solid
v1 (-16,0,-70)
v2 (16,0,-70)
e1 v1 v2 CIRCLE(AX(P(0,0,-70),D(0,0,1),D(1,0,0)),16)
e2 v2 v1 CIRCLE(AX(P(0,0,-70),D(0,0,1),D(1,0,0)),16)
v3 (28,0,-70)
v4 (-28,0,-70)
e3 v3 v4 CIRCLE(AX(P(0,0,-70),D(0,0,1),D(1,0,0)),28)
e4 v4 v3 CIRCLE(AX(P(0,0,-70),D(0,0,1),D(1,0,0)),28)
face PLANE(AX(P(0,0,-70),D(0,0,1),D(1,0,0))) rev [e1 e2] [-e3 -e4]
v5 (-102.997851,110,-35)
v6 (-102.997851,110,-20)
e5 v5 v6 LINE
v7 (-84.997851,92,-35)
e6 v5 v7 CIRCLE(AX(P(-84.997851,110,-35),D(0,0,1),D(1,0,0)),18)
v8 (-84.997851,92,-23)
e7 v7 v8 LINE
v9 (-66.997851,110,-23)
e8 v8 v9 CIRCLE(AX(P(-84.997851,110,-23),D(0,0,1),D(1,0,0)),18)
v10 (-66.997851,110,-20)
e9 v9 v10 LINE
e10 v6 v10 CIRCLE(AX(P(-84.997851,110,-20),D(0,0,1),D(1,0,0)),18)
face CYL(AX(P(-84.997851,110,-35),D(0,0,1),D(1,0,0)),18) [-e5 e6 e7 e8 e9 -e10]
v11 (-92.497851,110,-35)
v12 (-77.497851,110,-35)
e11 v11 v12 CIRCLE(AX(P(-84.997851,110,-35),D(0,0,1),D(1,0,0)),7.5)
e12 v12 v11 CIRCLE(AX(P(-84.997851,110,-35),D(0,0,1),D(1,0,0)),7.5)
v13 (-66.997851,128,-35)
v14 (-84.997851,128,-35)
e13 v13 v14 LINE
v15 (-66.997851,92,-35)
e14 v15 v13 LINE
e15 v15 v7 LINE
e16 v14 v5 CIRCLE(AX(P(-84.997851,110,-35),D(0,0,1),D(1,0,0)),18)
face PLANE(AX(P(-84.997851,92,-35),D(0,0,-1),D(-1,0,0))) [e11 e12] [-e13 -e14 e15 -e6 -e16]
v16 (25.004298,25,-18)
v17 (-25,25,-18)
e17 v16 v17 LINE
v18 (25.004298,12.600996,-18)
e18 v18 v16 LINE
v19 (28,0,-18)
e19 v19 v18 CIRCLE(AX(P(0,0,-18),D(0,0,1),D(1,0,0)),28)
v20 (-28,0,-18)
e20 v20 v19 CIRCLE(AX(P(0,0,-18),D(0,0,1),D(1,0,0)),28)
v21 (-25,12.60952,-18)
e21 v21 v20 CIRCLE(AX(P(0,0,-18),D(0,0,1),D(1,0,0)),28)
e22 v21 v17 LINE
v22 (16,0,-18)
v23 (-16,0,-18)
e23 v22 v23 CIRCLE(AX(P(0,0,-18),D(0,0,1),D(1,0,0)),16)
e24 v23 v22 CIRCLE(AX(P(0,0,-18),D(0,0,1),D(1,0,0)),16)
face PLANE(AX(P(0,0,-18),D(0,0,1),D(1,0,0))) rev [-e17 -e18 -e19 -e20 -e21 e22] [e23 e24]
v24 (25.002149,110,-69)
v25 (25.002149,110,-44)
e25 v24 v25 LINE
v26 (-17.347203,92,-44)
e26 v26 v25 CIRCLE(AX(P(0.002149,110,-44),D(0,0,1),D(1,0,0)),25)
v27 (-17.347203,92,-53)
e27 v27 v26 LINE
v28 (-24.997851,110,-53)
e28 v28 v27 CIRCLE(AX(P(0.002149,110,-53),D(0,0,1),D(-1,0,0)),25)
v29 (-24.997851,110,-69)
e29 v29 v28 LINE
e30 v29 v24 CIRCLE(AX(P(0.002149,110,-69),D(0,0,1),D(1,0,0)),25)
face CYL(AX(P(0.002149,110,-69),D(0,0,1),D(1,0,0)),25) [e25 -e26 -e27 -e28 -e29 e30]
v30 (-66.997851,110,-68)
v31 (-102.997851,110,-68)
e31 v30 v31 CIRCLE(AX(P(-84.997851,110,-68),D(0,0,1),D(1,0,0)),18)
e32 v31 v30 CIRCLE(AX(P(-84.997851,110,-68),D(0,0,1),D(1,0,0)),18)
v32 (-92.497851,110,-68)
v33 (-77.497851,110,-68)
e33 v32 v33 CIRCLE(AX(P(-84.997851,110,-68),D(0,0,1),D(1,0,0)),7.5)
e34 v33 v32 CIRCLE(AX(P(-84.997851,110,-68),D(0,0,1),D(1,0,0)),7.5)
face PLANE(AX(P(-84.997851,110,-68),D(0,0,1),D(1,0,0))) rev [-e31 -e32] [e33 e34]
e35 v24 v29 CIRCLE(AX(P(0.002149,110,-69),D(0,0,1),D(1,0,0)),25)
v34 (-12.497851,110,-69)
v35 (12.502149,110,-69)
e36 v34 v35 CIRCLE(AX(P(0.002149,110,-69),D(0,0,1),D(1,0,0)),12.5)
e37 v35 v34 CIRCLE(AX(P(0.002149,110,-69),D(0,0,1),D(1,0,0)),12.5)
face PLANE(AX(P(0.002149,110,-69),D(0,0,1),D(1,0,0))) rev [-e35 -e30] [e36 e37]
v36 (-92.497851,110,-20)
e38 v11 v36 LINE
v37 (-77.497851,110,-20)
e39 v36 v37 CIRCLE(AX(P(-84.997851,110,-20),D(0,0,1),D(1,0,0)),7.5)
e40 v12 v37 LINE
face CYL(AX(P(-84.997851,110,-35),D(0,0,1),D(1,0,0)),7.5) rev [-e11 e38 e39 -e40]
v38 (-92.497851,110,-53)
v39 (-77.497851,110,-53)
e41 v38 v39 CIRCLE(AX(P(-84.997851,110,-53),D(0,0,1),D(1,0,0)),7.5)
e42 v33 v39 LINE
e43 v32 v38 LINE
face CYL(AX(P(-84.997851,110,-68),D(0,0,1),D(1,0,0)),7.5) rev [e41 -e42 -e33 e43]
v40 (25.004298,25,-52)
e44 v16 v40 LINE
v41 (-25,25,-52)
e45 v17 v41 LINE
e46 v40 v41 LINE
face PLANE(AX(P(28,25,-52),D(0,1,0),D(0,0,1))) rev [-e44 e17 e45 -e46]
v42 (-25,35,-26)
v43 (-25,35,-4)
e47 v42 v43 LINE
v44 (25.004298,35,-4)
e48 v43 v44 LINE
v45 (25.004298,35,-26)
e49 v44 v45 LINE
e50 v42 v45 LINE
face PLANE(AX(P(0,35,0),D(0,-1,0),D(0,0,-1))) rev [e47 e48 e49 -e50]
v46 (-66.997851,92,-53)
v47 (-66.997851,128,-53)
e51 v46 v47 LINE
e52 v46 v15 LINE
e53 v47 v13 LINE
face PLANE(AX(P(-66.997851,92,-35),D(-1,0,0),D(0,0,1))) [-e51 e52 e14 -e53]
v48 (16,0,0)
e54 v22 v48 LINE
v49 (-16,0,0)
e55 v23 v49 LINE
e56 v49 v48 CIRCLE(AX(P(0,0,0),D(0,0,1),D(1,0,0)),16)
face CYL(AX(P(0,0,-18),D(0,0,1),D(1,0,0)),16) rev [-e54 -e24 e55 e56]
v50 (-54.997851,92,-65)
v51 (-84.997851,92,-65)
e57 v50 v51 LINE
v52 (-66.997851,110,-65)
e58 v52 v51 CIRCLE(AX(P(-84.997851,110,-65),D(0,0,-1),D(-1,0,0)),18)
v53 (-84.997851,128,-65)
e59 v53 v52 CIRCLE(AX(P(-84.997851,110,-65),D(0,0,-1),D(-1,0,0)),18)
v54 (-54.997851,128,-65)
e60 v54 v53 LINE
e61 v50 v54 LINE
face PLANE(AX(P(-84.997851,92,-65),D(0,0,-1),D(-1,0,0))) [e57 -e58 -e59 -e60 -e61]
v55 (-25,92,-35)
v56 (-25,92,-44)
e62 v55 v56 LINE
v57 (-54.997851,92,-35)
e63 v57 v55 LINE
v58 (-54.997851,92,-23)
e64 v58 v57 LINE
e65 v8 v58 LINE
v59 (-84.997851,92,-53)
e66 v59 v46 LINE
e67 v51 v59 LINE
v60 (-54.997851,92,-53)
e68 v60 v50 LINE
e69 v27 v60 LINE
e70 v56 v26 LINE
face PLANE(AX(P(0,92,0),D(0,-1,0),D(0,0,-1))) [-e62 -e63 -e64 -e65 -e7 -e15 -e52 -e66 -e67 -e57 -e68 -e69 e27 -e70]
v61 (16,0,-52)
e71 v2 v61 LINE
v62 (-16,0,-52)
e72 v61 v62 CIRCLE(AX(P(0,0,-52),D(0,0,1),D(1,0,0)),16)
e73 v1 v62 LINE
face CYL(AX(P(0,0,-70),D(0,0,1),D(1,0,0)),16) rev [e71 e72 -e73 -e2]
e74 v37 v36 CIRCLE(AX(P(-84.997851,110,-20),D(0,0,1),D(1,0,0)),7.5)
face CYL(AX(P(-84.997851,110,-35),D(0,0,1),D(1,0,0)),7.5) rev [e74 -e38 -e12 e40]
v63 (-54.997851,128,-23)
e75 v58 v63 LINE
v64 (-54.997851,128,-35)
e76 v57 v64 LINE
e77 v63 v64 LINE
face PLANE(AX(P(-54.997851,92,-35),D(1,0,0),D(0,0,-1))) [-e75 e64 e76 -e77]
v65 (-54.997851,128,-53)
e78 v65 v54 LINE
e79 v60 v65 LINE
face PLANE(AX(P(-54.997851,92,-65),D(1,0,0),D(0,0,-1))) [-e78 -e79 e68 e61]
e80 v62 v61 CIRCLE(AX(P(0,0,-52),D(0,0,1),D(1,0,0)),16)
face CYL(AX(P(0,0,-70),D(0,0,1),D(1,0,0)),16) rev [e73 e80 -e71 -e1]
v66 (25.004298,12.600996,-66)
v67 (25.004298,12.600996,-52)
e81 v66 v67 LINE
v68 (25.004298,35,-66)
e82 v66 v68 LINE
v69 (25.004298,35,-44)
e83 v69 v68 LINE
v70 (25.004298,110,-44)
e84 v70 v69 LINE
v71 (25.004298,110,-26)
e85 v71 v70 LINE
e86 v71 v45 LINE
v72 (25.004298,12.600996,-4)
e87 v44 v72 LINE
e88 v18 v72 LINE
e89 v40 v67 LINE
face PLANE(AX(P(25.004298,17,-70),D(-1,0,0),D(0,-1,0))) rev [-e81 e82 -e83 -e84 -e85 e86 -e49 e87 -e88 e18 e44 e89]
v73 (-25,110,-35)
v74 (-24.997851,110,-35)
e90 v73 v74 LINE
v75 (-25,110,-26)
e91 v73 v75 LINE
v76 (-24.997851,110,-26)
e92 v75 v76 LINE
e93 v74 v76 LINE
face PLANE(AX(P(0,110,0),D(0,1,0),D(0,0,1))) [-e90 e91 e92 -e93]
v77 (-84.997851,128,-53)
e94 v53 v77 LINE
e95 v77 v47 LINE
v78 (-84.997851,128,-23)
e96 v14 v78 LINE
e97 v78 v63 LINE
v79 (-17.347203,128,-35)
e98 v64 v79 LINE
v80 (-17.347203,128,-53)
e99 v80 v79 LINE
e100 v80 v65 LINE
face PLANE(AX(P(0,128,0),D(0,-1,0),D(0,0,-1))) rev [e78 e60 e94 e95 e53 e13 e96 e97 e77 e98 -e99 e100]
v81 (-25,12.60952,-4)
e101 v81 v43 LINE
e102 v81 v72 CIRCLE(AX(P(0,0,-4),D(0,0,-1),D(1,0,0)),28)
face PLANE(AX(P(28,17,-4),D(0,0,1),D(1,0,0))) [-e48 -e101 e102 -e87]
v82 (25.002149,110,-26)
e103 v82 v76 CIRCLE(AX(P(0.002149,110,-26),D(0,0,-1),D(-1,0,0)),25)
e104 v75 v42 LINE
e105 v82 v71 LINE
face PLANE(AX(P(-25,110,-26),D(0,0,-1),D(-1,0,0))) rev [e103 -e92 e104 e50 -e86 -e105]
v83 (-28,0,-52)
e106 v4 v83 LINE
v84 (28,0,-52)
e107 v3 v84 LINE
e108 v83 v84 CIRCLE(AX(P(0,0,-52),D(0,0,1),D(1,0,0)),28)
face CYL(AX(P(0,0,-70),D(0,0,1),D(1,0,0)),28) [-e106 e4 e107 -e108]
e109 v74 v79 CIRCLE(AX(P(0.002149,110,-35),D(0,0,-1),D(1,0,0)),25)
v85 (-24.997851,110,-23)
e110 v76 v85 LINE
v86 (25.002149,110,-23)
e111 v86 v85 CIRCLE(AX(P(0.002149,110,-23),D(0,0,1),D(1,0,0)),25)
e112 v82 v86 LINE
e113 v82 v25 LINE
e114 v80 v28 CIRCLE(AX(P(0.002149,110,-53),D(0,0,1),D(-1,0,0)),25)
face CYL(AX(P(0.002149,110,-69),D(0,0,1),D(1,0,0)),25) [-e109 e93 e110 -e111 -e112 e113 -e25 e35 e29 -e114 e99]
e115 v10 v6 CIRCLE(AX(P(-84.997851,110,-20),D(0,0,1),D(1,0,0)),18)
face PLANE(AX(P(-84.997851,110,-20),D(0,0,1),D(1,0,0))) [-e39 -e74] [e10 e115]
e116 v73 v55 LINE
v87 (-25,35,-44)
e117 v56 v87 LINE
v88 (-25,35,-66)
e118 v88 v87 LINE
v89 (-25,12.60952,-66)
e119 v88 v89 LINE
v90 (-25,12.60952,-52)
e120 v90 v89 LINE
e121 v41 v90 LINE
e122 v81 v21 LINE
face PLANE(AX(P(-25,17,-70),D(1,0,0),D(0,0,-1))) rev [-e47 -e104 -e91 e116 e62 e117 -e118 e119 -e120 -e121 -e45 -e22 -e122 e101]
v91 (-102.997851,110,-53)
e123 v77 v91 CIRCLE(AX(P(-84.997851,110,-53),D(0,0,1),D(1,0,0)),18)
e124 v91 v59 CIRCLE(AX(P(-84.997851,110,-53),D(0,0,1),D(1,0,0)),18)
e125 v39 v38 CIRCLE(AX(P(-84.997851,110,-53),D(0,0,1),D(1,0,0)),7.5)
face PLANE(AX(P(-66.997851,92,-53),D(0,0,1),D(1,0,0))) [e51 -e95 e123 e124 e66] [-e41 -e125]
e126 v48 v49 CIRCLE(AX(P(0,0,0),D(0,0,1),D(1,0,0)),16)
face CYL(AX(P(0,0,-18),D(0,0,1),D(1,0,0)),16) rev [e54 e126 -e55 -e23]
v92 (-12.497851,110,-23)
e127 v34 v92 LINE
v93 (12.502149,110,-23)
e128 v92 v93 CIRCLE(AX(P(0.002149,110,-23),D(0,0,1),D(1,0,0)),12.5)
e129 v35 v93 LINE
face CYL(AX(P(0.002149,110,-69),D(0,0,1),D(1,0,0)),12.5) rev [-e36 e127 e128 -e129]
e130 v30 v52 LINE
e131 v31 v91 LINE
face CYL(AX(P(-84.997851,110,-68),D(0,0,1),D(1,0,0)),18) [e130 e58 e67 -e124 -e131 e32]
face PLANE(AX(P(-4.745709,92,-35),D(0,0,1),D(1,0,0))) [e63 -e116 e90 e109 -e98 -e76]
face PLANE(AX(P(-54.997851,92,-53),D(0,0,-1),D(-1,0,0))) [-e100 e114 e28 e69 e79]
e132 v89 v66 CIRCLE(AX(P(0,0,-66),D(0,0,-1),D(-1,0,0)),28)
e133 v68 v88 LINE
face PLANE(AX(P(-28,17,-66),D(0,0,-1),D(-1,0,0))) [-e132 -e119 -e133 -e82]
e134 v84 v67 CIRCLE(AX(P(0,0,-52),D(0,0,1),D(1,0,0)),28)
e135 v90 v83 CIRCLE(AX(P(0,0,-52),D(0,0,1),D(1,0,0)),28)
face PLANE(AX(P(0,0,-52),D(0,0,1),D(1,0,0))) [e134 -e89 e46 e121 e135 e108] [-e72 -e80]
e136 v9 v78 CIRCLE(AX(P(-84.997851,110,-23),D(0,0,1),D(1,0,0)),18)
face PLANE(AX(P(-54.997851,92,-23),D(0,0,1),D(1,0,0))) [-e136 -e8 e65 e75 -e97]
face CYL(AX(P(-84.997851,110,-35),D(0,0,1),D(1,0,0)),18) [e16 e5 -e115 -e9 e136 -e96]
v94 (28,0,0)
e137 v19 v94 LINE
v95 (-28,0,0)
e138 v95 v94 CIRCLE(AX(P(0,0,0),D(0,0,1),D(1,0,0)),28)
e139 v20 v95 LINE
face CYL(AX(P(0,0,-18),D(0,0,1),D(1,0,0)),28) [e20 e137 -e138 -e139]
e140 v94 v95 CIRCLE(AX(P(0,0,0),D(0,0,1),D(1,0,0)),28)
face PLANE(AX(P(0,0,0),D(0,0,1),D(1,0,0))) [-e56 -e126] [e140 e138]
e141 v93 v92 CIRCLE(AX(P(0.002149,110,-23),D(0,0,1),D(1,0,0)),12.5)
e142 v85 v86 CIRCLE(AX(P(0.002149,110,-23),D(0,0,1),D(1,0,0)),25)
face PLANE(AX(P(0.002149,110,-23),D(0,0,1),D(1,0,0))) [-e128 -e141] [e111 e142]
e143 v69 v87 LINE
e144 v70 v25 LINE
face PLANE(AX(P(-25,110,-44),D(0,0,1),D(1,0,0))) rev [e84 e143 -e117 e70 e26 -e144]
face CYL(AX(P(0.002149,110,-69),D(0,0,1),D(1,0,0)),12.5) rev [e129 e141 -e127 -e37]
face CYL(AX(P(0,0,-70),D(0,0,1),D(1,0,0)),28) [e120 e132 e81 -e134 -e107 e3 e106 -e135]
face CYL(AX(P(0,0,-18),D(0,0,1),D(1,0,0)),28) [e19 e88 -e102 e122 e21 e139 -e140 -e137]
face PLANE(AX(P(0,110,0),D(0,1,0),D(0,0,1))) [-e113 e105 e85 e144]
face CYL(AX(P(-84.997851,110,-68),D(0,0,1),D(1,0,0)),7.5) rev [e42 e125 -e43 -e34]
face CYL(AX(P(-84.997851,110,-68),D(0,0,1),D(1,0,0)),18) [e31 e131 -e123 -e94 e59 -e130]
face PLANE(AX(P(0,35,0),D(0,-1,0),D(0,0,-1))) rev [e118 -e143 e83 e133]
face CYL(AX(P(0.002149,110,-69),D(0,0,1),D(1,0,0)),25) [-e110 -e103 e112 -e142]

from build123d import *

# Parameters (mm, degrees)
FRONT_PIVOT_EYE_SKETCH_R        = 28
FRONT_PIVOT_EYE_SKETCH_R_2      = 16
FRONT_PIVOT_EYE_56X_32_DEPTH    = 18
REAR_PIVOT_EYE_SKETCH_R         = 28
REAR_PIVOT_EYE_SKETCH_R_2       = 16
REAR_PIVOT_EYE_56X_32_DEPTH     = 18
LOWER_CLEVIS_BLOCK_48X48_DEPTH  = 18
CLEVIS_BLOCK_RELIEF_SKETCH_W    = 3
CLEVIS_BLOCK_RELIEF_SKETCH_H    = 18
CLEVIS_BLOCK_RELIEF_CUT_DEPTH   = 80.780950107
LOWER_CLEVIS_SLOT_SKETCH_W      = 34
LOWER_CLEVIS_SLOT_SKETCH_H      = 8
LOWER_CLEVIS_SLOT_34X8_DEPTH    = 95.519839187
LOWER_WEB_PLATE_SKETCH_W        = 2.751404539
LOWER_WEB_PLATE_SKETCH_H        = 14
LOWER_WEB_PLATE_SKETCH_W_2      = 2.75570227
LOWER_WEB_PLATE_5MM_DEPTH       = 5
MAIN_ARM_SKETCH_W               = 50.004297731
MAIN_ARM_SKETCH_H               = 18
MAIN_ARM_9X18_DEPTH             = 75
UPPER_PIVOT_HUB_SKETCH_R        = 25
UPPER_PIVOT_HUB_SKETCH_R_2      = 12.5
UPPER_PIVOT_HUB_50X_25_DEPTH    = 46
HUB_BORE_SKETCH_R               = 12.5
HUB_BORE_THROUGH_CUT_25_DEPTH   = 145.723875017
UPPER_ARM_SKETCH_R              = 18
UPPER_ARM_SKETCH_R_2            = 7.5
UPPER_ARM_36X15_DEPTH           = 15
UPPER_ARM_EXTENSION_SKETCH_R    = 18
UPPER_ARM_EXTENSION_SKETCH_R_2  = 7.5
UPPER_ARM_EXTENSION_36X15_DEPTH = 15
UPPER_CLEVIS_HEAD_DEPTH         = 36
UPPER_CLEVIS_SLOT_SKETCH_R      = 12.5
UPPER_CLEVIS_SLOT_SKETCH_R_2    = 7.5
UPPER_CLEVIS_SLOT_25_DEPTH      = 177.188981887


with BuildPart() as part:
    # Front Pivot Eye Sketch → Front Pivot Eye Ø56xØ32 (new body)
    with BuildSketch(Plane.XY):
        Circle(FRONT_PIVOT_EYE_SKETCH_R)
        Circle(FRONT_PIVOT_EYE_SKETCH_R_2, mode=Mode.SUBTRACT)
    extrude(amount=-FRONT_PIVOT_EYE_56X_32_DEPTH)



with BuildPart() as body_2:
    # Rear Pivot Eye Sketch → Rear Pivot Eye Ø56xØ32 (new body)
    with BuildSketch(Plane.XY.offset(-52)):
        Circle(REAR_PIVOT_EYE_SKETCH_R)
        Circle(REAR_PIVOT_EYE_SKETCH_R_2, mode=Mode.SUBTRACT)
    extrude(amount=-REAR_PIVOT_EYE_56X_32_DEPTH)


with BuildPart() as part_1:
    add(part.part)

    add(body_2.part)  # Lower Clevis Block 48x48 merges body 2
    # Lower Clevis Block Sketch → Lower Clevis Block 48x48 (add)
    with BuildSketch(Plane(origin=(0, 35, 0), x_dir=(1, 0, 0), z_dir=(0, 1, 0))):
        Polygon((-28, 52), (-28, 66), (28, 66), (28, 18), (28, 4), (-28, 4), align=None)
    extrude(amount=-LOWER_CLEVIS_BLOCK_48X48_DEPTH)

    # Clevis Block Relief Sketch → Clevis Block Relief Cut (cut, through all)
    with BuildSketch(Plane.XY.offset(-4)):
        with Locations((-26.5, 26)):
            Rectangle(CLEVIS_BLOCK_RELIEF_SKETCH_W, CLEVIS_BLOCK_RELIEF_SKETCH_H)
        Polygon((28, 17), (25.124297731, 17), (25.004297731, 17), (25.004297731, 35), (28, 35), align=None)
    extrude(amount=-CLEVIS_BLOCK_RELIEF_CUT_DEPTH, mode=Mode.SUBTRACT)

    # Lower Clevis Slot Sketch → Lower Clevis Slot 34x8 (cut, through all)
    with BuildSketch(Plane.ZY.offset(25)):
        with Locations((-35, 21)):
            Rectangle(LOWER_CLEVIS_SLOT_SKETCH_W, LOWER_CLEVIS_SLOT_SKETCH_H)
    extrude(amount=-LOWER_CLEVIS_SLOT_34X8_DEPTH, mode=Mode.SUBTRACT)

    # Lower Web Plate Sketch → Lower Web Plate 5mm (add)
    with BuildSketch(Plane.XZ.offset(-17)):
        with Locations((-23.624297731, -59)):
            Rectangle(LOWER_WEB_PLATE_SKETCH_W, LOWER_WEB_PLATE_SKETCH_H)
        with Locations((-23.624297731, -11)):
            Rectangle(LOWER_WEB_PLATE_SKETCH_W, LOWER_WEB_PLATE_SKETCH_H)
        with Locations((23.626446596, -11)):
            Rectangle(LOWER_WEB_PLATE_SKETCH_W_2, LOWER_WEB_PLATE_SKETCH_H)
        with Locations((23.626446596, -59)):
            Rectangle(LOWER_WEB_PLATE_SKETCH_W_2, LOWER_WEB_PLATE_SKETCH_H)
    extrude(amount=LOWER_WEB_PLATE_5MM_DEPTH)

    # Main Arm Sketch → Main Arm 9x18 (add)
    with BuildSketch(Plane(origin=(0, 35, 0), x_dir=(1, 0, 0), z_dir=(0, 1, 0))):
        with Locations((0.002148866, 35)):
            Rectangle(MAIN_ARM_SKETCH_W, MAIN_ARM_SKETCH_H)
    extrude(amount=MAIN_ARM_9X18_DEPTH)

    # Upper Pivot Hub Sketch → Upper Pivot Hub Ø50xØ25 (add)
    with BuildSketch(Plane.XY.offset(-23)):
        with Locations((0.002148865, 110)):
            Circle(UPPER_PIVOT_HUB_SKETCH_R)
        with Locations((0.002148865, 110)):
            Circle(UPPER_PIVOT_HUB_SKETCH_R_2, mode=Mode.SUBTRACT)
    extrude(amount=-UPPER_PIVOT_HUB_50X_25_DEPTH)

    # Hub Bore Sketch → Hub Bore Through Cut Ø25 (cut, through all)
    with BuildSketch(Plane.XY.offset(-26)):
        with Locations((0.002148865, 110)):
            Circle(HUB_BORE_SKETCH_R)
    extrude(amount=-HUB_BORE_THROUGH_CUT_25_DEPTH, mode=Mode.SUBTRACT)



with BuildPart() as body_2_2:
    # Upper Arm Sketch → Upper Arm 36x15 (new body)
    with BuildSketch(Plane.XY.offset(-20)):
        with Locations((-84.997851135, 110)):
            Circle(UPPER_ARM_SKETCH_R)
        with Locations((-84.997851135, 110)):
            Circle(UPPER_ARM_SKETCH_R_2, mode=Mode.SUBTRACT)
    extrude(amount=-UPPER_ARM_36X15_DEPTH)


with BuildPart() as body_3:
    # Upper Arm Extension Sketch → Upper Arm Extension 36x15 (new body)
    with BuildSketch(Plane.XY.offset(-53)):
        with Locations((-84.997851135, 110)):
            Circle(UPPER_ARM_EXTENSION_SKETCH_R)
        with Locations((-84.997851135, 110)):
            Circle(UPPER_ARM_EXTENSION_SKETCH_R_2, mode=Mode.SUBTRACT)
    extrude(amount=-UPPER_ARM_EXTENSION_36X15_DEPTH)


with BuildPart() as part_2:
    add(part_1.part)

    add(body_2_2.part)  # Upper Clevis Head merges body 2 2

    add(body_3.part)  # Upper Clevis Head merges body 3
    # Upper Clevis Head Sketch → Upper Clevis Head (add)
    with BuildSketch(Plane(origin=(0, 128, 0), x_dir=(1, 0, 0), z_dir=(0, 1, 0))):
        Polygon((-84.997851135, 53), (-84.997851135, 65), (-54.997851135, 65), (-54.997851135, 53), (-4.745708578, 53), (-4.745708578, 35), (-54.997851135, 35), (-54.997851135, 23), (-84.997851135, 23), (-84.997851135, 35), (-66.997851135, 35), (-66.997851135, 53), align=None)
    extrude(amount=-UPPER_CLEVIS_HEAD_DEPTH)

    # Upper Clevis Slot Sketch → Upper Clevis Slot 25 (cut, through all)
    with BuildSketch(Plane.XY.offset(-23)):
        with Locations((0.002148865, 110)):
            Circle(UPPER_CLEVIS_SLOT_SKETCH_R)
        with Locations((-84.997851135, 110)):
            Circle(UPPER_CLEVIS_SLOT_SKETCH_R_2)
    extrude(amount=-UPPER_CLEVIS_SLOT_25_DEPTH, mode=Mode.SUBTRACT)


solid = part_2.part
